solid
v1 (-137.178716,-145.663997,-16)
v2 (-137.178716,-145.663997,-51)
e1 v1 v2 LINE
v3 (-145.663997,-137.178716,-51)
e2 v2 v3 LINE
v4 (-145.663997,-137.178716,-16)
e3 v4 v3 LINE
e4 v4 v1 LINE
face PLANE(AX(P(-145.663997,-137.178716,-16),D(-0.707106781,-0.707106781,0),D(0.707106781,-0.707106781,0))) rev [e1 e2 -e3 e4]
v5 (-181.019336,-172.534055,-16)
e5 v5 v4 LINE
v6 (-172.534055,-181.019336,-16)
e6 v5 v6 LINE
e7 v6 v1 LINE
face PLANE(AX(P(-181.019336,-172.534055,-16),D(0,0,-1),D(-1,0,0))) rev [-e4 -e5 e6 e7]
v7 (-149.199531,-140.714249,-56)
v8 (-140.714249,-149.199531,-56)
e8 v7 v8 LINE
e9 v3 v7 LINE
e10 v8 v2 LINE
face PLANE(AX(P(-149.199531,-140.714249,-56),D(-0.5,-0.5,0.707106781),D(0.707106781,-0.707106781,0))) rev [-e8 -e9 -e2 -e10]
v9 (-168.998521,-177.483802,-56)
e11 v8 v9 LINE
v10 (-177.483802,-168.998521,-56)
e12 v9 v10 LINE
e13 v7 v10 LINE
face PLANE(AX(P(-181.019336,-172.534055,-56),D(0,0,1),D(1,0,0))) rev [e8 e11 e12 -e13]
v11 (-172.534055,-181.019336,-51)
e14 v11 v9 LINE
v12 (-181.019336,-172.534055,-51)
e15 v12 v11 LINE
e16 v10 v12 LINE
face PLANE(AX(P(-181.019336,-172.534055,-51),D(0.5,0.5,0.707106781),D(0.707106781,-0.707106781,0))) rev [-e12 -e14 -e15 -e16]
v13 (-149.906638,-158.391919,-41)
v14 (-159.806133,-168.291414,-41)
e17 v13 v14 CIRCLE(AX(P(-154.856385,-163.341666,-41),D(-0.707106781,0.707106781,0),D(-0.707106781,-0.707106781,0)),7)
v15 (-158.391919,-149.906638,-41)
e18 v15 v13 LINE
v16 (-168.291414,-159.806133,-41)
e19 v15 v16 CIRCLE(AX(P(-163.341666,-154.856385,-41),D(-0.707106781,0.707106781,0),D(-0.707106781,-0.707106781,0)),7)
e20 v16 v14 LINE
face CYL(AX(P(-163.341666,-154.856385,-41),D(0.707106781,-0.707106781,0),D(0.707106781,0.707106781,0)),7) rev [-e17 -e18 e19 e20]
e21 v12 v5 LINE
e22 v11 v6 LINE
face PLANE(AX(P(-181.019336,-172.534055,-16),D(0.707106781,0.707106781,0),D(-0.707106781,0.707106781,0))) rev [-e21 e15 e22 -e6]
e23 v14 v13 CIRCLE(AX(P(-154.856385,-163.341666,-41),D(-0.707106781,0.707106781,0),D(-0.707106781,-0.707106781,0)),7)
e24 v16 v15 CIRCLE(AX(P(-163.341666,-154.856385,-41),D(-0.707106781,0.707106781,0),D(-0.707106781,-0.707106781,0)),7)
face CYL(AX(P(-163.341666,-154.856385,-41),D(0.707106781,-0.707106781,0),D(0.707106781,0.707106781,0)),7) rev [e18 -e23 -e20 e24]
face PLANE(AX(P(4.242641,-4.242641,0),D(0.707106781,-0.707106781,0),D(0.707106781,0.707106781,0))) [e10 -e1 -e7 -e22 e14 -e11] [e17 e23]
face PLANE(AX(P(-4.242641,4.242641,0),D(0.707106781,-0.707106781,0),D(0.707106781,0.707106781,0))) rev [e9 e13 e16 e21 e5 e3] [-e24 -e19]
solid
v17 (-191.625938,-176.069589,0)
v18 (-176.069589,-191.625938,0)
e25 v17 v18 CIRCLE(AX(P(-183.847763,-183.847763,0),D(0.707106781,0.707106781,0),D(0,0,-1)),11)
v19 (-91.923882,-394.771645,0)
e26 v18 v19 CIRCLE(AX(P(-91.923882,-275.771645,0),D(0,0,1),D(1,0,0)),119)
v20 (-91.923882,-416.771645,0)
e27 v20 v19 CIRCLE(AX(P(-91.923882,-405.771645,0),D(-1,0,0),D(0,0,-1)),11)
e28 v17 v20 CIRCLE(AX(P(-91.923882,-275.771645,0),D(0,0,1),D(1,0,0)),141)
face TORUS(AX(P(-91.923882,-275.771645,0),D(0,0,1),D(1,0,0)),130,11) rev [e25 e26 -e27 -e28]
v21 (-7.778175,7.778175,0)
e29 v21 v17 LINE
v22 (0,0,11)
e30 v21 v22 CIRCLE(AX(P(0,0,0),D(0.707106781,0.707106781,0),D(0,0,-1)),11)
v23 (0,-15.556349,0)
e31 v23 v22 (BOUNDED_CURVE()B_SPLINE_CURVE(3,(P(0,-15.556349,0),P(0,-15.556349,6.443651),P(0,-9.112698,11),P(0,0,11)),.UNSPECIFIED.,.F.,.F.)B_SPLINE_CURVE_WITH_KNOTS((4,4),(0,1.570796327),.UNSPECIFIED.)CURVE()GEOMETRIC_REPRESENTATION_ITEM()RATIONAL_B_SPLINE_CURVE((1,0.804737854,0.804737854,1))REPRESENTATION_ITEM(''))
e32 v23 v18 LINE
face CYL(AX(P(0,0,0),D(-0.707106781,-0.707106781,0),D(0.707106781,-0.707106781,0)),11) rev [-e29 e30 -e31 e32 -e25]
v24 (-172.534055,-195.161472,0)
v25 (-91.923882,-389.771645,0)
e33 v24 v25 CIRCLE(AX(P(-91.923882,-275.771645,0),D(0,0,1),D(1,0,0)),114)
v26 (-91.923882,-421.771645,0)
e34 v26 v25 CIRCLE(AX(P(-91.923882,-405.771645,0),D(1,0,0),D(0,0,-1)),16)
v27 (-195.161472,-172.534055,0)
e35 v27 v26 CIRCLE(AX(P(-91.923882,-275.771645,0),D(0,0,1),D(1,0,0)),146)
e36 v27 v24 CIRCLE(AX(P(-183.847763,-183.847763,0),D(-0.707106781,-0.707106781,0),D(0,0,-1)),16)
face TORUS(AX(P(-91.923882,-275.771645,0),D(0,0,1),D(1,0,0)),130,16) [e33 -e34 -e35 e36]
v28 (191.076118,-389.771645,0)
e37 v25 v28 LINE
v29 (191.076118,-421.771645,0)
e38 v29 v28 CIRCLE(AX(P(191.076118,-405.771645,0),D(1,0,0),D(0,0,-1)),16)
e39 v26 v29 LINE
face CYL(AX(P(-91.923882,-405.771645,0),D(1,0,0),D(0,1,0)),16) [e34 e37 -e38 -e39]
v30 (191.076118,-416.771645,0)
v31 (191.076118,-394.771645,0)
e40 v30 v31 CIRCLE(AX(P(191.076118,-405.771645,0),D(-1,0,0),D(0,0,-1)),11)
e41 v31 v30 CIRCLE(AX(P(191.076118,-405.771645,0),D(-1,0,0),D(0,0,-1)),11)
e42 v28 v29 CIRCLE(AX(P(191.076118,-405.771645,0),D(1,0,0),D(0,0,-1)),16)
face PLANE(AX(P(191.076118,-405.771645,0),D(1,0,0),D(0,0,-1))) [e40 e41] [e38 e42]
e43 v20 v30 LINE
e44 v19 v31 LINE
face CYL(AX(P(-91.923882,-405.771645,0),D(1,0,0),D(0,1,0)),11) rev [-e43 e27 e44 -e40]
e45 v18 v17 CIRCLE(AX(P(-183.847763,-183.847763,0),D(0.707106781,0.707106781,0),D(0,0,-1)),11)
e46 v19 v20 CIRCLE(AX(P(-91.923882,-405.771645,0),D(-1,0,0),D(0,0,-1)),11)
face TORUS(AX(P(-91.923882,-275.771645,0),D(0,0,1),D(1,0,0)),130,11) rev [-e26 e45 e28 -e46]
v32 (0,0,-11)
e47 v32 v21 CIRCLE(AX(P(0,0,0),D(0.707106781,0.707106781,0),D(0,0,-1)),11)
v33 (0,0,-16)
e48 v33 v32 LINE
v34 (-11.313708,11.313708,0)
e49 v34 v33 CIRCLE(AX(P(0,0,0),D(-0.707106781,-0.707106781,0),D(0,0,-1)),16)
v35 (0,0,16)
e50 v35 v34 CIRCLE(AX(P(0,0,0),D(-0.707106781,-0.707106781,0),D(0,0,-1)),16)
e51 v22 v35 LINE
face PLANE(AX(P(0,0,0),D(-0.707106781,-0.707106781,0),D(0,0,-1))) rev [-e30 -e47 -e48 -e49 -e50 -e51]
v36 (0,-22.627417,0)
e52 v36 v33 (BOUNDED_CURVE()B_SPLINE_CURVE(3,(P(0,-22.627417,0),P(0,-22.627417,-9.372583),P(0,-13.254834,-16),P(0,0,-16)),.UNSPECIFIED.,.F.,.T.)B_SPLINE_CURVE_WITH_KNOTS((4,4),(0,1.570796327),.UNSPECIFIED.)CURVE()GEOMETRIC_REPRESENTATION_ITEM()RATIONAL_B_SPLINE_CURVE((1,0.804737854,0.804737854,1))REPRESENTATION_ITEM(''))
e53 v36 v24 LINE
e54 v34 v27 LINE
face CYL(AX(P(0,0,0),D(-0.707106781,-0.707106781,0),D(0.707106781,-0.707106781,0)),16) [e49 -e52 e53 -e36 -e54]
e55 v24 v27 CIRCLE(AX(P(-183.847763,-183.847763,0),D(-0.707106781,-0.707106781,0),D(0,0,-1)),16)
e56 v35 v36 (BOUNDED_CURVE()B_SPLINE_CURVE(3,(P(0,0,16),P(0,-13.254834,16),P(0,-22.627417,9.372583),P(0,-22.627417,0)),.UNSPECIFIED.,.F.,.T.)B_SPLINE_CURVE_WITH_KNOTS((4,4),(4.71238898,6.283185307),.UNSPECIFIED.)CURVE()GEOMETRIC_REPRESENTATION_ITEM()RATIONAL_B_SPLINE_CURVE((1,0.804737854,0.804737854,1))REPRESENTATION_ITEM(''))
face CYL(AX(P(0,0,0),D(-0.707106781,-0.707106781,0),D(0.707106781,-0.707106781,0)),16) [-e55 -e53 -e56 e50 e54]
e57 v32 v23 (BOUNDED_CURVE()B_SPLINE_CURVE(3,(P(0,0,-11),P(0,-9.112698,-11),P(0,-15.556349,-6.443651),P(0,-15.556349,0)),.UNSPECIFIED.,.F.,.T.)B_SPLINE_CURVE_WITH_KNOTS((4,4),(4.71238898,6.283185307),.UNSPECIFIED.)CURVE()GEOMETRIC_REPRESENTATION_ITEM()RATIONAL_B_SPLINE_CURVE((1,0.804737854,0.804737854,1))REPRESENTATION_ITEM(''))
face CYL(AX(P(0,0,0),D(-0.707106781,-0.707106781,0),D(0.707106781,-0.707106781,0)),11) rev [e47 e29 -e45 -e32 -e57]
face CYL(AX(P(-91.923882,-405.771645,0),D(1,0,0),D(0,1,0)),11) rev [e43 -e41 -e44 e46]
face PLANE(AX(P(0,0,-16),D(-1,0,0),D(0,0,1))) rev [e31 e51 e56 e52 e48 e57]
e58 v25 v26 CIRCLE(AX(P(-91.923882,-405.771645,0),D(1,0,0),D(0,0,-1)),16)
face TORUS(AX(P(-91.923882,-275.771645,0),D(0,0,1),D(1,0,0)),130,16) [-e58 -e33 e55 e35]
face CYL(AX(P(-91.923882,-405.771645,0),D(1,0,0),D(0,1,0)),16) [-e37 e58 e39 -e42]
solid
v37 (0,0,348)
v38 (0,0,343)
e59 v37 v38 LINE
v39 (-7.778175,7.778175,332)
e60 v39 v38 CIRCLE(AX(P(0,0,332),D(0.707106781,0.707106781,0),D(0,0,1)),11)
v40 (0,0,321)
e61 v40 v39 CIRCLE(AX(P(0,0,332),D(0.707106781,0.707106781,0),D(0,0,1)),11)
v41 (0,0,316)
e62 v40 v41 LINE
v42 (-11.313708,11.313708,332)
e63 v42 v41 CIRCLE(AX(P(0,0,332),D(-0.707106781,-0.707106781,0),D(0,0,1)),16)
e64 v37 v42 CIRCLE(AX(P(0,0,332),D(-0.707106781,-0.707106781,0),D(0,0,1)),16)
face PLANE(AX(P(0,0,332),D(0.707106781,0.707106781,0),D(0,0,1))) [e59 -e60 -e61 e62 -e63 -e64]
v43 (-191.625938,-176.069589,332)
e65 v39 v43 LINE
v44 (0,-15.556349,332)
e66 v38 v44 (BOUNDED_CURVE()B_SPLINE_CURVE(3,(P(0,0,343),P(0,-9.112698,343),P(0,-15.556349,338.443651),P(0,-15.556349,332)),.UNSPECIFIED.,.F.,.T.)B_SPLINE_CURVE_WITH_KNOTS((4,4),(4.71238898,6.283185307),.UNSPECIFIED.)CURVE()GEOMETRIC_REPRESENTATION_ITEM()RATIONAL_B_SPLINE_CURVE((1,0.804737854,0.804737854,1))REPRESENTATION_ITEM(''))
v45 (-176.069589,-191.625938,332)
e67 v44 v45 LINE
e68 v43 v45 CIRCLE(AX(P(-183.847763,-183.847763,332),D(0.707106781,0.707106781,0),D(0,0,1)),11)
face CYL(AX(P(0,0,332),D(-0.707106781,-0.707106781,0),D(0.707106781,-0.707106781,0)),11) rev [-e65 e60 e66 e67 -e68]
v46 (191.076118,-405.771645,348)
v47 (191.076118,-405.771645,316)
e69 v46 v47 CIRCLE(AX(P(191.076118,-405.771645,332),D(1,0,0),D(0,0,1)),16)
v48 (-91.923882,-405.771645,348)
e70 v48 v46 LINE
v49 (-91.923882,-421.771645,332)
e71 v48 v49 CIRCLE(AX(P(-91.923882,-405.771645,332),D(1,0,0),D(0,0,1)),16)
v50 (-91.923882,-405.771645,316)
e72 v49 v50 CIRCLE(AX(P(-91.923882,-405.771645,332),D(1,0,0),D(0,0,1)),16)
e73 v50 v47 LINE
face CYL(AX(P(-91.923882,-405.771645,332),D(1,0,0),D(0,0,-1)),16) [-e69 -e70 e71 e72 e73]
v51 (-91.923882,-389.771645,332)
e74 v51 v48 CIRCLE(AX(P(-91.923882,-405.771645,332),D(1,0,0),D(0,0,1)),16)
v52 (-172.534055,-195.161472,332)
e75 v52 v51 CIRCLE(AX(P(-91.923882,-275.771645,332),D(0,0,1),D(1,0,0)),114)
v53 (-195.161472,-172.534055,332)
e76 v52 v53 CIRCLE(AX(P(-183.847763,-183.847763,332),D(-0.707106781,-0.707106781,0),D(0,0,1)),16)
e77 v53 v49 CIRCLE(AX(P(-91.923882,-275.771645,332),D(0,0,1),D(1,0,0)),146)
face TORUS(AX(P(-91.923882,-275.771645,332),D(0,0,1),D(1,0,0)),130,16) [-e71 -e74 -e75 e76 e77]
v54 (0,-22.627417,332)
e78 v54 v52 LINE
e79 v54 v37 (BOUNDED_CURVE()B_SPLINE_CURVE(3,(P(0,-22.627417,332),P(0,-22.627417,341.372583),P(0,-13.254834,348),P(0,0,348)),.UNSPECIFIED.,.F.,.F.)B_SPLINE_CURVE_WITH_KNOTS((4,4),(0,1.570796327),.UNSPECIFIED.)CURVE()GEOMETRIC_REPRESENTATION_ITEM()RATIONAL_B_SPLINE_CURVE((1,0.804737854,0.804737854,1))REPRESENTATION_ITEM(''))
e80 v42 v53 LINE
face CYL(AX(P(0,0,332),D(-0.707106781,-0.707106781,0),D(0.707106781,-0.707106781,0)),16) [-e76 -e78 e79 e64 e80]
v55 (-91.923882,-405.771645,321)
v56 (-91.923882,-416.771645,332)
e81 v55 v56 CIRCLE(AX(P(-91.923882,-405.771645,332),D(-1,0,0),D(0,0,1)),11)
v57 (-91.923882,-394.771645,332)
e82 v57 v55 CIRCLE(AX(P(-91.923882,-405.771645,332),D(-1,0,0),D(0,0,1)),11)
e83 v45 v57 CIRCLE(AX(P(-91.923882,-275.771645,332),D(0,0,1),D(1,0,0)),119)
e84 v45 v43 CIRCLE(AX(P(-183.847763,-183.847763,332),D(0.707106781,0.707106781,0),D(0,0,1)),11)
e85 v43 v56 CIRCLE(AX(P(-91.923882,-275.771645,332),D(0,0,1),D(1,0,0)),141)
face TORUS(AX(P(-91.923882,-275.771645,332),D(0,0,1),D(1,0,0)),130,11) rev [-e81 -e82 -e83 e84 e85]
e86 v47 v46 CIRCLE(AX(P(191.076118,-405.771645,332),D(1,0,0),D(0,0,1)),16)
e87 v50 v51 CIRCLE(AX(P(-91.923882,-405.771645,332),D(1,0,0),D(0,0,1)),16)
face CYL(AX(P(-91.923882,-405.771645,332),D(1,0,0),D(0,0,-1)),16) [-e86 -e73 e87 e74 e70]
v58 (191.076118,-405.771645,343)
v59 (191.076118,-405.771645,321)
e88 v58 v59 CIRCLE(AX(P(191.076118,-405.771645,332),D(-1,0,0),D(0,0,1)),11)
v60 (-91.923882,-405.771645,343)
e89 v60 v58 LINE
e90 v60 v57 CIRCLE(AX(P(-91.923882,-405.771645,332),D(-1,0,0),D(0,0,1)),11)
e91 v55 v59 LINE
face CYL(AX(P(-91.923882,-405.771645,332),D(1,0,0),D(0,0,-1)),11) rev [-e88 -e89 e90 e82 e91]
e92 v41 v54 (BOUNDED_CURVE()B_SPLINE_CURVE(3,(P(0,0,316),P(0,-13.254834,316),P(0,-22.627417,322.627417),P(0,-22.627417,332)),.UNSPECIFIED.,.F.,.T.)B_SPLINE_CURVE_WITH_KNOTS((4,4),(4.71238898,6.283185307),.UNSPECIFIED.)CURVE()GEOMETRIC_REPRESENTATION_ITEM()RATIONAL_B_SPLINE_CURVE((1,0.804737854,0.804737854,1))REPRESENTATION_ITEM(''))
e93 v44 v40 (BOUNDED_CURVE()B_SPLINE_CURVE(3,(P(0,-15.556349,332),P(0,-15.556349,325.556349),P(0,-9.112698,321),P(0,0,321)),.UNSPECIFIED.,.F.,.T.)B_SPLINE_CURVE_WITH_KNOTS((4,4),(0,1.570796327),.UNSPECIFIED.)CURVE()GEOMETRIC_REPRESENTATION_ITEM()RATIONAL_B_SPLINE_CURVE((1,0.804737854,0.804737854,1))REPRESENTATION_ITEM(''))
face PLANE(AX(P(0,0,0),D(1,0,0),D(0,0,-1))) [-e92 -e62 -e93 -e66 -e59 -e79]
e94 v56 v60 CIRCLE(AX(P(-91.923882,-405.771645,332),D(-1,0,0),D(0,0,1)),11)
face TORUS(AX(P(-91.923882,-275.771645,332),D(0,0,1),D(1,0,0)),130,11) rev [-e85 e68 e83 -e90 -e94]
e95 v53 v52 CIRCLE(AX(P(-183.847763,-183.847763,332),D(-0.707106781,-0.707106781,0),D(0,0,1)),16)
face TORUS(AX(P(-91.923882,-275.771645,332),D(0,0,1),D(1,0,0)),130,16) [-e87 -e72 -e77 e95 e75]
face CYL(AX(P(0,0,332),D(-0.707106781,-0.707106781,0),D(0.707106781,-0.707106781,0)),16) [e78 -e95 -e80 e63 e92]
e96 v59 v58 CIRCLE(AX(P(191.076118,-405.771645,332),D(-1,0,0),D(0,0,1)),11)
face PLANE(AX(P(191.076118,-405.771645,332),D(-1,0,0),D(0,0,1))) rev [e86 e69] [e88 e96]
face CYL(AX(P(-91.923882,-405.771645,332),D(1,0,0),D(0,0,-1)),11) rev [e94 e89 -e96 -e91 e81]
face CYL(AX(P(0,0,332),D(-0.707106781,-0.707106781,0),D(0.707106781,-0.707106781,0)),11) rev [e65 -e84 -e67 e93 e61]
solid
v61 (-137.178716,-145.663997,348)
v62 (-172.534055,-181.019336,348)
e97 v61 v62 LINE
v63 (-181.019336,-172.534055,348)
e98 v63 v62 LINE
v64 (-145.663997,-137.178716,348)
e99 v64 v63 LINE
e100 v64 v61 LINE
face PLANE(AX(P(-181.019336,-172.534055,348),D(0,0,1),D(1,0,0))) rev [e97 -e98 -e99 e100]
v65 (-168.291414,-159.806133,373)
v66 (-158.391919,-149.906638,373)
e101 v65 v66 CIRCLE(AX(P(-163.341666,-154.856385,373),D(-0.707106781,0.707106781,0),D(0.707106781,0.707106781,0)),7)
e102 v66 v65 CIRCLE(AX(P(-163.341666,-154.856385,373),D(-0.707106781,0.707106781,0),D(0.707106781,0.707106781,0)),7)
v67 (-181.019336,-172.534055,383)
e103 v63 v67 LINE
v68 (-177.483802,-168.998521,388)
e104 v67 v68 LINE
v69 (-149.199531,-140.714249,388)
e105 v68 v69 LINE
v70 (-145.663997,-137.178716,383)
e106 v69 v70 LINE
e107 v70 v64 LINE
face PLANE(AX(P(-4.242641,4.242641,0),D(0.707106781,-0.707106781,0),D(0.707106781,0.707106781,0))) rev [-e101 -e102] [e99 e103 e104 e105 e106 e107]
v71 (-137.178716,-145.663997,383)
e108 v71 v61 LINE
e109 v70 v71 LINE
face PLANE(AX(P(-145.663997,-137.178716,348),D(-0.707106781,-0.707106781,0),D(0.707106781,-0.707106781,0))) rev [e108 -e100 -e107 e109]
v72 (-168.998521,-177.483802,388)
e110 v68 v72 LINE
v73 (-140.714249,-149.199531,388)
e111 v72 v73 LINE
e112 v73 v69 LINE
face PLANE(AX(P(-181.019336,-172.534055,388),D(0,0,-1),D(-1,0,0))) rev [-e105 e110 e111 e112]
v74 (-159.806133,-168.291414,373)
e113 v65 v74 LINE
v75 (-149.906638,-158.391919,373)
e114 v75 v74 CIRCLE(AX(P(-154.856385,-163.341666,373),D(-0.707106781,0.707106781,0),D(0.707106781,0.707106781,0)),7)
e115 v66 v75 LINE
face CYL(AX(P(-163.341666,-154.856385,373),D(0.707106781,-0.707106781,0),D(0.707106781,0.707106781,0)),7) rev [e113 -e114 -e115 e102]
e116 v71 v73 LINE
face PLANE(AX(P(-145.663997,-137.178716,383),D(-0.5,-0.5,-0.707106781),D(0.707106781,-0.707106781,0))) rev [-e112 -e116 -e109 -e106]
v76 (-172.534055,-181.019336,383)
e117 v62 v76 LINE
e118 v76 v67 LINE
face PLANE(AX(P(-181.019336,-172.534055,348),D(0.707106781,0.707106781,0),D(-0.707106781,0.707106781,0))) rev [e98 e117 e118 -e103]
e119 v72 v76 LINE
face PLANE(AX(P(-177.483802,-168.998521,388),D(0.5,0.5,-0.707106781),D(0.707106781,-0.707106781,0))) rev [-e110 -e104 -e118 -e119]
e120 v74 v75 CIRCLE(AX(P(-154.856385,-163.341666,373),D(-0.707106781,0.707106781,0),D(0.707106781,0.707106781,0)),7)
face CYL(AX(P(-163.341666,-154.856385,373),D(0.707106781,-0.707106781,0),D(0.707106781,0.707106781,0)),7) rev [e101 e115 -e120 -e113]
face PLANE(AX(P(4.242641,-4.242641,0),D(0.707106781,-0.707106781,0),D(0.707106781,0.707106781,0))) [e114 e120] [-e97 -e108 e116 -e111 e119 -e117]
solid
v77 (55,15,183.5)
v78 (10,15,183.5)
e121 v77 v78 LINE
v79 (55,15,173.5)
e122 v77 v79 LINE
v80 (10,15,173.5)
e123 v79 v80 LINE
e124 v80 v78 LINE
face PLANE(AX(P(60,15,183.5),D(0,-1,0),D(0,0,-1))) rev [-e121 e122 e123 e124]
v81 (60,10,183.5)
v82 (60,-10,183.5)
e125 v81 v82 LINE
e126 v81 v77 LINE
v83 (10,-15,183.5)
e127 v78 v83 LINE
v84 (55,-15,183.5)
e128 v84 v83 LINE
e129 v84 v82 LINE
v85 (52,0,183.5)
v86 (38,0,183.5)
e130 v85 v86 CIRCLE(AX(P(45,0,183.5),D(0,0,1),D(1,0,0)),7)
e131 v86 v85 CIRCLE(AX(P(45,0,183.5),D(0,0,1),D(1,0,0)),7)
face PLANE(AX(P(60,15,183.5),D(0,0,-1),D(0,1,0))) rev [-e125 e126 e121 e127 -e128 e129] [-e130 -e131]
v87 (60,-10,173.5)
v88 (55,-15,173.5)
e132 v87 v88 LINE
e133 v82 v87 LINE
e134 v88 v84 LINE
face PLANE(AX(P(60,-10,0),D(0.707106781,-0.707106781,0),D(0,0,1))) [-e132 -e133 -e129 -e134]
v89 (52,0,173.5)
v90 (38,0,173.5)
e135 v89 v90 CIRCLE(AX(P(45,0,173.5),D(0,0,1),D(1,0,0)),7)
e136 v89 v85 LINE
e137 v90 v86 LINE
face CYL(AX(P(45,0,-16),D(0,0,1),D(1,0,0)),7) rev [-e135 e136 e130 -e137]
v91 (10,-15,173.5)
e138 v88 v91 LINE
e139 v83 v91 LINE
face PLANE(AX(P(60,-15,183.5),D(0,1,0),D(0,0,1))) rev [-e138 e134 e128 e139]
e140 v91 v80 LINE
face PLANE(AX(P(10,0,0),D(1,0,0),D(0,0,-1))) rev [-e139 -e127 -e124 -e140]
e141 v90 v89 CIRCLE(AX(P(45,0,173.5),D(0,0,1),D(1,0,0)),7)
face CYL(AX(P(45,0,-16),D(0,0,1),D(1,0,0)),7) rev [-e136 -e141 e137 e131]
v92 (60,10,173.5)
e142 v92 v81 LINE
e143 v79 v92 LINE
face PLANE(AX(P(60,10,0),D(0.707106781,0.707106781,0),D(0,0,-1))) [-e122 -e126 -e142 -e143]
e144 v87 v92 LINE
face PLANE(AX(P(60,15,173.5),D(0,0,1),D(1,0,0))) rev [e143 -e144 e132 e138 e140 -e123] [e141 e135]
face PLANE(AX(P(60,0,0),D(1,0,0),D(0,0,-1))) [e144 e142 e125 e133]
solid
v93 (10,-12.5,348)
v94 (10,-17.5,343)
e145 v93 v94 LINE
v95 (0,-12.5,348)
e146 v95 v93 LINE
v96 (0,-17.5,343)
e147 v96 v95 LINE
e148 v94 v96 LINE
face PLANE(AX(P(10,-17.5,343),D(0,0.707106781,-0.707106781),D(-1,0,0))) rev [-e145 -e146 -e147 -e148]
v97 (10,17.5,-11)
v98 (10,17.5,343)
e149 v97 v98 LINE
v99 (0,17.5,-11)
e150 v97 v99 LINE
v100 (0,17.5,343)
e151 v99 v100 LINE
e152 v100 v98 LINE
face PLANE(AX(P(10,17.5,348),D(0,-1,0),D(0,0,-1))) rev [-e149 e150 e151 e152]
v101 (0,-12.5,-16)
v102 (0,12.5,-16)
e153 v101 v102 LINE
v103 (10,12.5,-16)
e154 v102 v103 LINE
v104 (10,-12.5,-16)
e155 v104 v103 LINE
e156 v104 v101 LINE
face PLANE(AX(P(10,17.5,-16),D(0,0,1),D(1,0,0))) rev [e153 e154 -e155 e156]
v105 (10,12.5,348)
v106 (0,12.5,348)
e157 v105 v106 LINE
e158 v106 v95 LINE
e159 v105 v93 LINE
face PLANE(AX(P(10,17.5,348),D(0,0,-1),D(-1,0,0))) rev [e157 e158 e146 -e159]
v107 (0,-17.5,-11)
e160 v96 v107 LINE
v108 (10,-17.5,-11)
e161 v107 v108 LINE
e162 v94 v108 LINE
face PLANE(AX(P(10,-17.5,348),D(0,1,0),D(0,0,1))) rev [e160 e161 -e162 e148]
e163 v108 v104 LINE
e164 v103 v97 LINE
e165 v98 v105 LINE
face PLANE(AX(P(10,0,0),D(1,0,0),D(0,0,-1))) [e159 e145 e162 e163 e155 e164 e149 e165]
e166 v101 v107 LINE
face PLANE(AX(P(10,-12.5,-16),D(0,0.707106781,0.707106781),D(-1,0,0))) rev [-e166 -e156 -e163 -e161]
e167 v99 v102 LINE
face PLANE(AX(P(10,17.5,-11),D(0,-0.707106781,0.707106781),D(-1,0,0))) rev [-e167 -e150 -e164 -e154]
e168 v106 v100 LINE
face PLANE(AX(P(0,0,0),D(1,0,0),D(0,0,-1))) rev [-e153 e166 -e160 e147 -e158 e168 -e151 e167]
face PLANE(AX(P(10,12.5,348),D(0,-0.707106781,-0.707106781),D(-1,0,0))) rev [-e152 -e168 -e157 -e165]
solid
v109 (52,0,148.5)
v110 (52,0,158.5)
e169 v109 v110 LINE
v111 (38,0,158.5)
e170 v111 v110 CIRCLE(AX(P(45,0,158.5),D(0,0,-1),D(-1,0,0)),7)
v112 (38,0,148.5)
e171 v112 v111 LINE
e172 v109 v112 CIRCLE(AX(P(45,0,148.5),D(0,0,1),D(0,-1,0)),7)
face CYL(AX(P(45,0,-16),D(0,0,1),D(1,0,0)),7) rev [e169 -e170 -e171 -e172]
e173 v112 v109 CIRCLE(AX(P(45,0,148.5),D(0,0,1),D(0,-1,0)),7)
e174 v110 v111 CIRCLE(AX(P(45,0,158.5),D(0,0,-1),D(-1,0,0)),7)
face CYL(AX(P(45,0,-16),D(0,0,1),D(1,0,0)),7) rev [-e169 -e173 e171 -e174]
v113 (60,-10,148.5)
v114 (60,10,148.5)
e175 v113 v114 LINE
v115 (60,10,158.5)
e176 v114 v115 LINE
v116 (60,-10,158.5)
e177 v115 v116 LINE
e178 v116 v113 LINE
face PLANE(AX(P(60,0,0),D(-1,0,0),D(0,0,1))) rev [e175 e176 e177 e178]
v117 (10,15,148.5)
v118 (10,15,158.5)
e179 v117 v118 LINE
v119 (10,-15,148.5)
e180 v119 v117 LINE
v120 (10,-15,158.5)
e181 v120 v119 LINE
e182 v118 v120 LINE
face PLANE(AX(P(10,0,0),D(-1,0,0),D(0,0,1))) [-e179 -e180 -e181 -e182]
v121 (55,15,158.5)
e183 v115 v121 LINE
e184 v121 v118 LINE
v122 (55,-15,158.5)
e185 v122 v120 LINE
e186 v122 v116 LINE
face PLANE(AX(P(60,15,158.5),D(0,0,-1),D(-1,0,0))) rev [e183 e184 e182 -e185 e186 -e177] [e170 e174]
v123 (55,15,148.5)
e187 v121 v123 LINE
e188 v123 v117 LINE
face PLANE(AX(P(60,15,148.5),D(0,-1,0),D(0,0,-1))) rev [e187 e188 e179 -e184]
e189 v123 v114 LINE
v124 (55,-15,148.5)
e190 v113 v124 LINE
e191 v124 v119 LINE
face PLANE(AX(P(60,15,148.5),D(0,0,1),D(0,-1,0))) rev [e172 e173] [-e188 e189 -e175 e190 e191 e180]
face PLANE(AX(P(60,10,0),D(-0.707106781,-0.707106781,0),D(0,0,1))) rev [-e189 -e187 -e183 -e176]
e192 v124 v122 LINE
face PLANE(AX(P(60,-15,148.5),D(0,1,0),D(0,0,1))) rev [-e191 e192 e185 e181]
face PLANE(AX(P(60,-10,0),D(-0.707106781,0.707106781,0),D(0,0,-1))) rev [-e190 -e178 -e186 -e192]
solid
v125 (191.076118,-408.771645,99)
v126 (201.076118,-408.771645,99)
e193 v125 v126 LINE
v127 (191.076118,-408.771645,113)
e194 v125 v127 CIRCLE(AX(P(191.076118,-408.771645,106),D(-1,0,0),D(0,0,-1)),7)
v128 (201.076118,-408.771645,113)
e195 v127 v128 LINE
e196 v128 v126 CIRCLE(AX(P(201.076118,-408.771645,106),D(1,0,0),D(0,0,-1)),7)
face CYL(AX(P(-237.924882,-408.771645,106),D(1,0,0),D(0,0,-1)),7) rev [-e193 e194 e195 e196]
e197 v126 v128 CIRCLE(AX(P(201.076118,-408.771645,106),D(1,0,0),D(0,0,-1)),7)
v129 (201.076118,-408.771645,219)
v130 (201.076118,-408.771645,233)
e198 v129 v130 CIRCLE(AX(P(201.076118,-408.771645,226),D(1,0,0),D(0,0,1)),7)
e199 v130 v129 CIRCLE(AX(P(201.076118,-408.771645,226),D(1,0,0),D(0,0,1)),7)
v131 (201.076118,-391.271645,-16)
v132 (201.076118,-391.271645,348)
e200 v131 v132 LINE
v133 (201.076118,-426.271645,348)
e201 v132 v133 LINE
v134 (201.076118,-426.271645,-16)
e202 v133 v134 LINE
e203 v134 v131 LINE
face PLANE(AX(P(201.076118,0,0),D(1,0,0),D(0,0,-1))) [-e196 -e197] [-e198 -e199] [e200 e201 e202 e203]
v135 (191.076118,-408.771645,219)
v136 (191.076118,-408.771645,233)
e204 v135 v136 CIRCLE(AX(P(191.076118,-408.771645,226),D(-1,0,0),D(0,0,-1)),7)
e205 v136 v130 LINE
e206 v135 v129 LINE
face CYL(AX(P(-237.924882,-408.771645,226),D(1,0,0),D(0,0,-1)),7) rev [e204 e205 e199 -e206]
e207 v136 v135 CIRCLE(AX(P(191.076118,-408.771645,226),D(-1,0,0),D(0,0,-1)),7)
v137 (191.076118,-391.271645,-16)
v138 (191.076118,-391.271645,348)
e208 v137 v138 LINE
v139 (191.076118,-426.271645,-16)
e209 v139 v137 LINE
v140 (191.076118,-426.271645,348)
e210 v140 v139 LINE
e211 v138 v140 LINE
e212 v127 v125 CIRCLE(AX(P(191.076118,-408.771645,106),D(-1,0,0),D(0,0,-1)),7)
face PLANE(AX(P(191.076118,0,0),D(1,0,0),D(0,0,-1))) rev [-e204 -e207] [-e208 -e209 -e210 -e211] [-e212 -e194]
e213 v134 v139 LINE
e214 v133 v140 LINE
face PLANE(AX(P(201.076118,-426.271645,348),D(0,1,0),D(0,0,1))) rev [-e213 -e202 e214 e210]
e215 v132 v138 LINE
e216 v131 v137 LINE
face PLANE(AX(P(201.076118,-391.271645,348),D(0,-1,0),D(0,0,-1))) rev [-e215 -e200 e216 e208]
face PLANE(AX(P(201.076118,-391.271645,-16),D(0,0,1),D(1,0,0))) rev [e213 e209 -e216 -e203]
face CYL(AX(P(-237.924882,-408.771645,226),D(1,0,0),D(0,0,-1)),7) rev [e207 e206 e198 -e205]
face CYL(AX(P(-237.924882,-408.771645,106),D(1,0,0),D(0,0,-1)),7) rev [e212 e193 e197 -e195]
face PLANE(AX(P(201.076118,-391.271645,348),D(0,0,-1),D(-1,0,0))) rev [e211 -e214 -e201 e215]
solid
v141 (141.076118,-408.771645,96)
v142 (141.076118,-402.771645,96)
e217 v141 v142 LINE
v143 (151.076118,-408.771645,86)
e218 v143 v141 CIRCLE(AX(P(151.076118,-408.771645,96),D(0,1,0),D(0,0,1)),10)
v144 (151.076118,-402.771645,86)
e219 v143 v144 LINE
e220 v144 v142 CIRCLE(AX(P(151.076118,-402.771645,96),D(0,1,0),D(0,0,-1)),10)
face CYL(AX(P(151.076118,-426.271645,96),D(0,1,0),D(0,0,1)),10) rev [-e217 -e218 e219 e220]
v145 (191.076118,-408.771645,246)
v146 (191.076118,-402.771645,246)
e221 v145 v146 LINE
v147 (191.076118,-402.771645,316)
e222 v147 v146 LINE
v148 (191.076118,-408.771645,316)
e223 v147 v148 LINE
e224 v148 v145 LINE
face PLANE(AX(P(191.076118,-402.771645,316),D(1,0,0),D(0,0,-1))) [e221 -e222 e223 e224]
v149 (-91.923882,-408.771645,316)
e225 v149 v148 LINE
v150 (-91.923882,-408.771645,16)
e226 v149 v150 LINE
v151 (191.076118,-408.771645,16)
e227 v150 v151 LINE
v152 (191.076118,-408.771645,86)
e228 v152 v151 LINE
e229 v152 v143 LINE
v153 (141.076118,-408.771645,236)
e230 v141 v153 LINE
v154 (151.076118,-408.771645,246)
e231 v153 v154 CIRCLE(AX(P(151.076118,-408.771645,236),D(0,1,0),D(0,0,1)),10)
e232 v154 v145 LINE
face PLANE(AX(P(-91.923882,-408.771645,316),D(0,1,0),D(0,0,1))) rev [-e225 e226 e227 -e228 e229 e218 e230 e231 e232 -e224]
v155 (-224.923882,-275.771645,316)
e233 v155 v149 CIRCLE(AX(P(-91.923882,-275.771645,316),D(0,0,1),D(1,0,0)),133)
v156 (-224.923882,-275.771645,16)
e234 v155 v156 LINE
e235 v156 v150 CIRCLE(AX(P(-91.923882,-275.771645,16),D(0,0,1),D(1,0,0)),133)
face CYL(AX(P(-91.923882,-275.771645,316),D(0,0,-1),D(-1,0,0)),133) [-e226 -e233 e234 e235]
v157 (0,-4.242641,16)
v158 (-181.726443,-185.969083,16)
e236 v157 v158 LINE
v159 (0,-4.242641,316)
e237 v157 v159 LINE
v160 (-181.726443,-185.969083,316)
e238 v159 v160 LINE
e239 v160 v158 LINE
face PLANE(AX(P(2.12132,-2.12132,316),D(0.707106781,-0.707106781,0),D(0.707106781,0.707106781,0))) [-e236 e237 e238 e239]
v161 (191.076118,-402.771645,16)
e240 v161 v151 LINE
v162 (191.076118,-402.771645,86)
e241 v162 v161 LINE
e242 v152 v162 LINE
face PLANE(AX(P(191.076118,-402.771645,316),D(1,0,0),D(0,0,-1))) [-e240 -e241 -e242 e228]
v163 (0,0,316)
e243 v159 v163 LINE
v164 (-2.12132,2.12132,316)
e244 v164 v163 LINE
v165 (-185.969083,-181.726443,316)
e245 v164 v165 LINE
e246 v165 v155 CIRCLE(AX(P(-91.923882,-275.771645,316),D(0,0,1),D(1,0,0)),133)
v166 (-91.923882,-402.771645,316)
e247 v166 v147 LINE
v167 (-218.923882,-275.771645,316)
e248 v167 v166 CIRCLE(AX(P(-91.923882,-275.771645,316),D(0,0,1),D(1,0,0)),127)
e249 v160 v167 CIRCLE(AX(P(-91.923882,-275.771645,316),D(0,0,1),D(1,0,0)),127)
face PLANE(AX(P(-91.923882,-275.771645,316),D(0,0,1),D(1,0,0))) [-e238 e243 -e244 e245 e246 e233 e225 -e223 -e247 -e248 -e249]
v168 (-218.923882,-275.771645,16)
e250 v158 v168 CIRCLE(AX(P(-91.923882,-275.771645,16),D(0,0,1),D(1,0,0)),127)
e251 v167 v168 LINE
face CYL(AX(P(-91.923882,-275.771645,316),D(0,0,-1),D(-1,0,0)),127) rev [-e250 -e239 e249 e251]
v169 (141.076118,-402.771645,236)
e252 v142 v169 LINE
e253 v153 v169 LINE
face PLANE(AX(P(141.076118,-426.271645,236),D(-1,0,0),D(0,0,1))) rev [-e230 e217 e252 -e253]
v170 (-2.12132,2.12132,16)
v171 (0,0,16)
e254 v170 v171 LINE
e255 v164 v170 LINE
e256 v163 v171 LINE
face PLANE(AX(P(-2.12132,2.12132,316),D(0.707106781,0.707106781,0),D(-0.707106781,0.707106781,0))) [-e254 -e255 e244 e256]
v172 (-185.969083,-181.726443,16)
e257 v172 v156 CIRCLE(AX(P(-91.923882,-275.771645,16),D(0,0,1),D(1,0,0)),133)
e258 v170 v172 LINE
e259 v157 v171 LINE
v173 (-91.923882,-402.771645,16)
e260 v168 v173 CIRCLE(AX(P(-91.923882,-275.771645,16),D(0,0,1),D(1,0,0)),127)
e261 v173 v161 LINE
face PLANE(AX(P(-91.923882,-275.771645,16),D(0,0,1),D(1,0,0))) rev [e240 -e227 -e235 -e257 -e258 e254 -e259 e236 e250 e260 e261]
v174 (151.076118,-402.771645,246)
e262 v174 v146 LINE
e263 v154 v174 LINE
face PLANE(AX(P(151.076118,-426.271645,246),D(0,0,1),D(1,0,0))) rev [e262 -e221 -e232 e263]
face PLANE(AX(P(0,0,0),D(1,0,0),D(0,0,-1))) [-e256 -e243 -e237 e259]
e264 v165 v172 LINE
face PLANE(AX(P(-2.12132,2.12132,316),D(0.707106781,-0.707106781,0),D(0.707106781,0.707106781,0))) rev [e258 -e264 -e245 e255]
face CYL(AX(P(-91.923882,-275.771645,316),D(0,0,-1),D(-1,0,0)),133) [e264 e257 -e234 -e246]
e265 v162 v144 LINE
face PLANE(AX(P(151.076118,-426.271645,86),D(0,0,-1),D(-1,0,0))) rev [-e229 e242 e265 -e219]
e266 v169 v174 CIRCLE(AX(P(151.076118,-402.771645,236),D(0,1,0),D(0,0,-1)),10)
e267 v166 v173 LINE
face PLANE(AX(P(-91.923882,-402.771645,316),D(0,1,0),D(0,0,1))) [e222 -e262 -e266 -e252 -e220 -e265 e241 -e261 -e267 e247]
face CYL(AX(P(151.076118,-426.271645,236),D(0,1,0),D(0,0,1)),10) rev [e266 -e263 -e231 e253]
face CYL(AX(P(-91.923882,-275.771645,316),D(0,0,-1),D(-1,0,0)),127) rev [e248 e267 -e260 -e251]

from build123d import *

# Parameters (mm, degrees)
SKETCH_2_R               = 16
SKETCH_2_R_2             = 11
CUT_EXTRUDE_1_DEPTH      = 485.515318427
CUT_EXTRUDE_1_DEPTH_BACK = 485.515318427
SKETCH_4_W               = 55.642342567
SKETCH_4_H               = 67.933254927
EXTRUDE_START            = 16
EXTRUDE_2_DEPTH          = 300
SKETCH_7_R               = 16
SKETCH_7_R_2             = 11
SKETCH_9_W               = 513.497861872
SKETCH_9_H               = 78.296499381
CUT_EXTRUDE_2_DEPTH      = 597.324654745
SKETCH_10_W              = 364
SKETCH_10_H              = 35
EXTRUDE_2_2_DEPTH        = 10
SKETCH_11_W              = 364
SKETCH_11_H              = 35
EXTRUDE_4_DEPTH          = 10
CHAMFER_1_SIZE           = 5
CUT_EXTRUDE_4_DEPTH      = 596.26467125
SKETCH_14_R              = 7
CUT_EXTRUDE_5_DEPTH      = 10
SKETCH_15_W              = 10
SKETCH_15_H              = 30
EXTRUDE_5_DEPTH          = 50
EXTRUDE_5_2_DEPTH        = 50
CHAMFER_2_SIZE           = 5
CHAMFER_3_SIZE           = 5
SKETCH_16_R              = 7
CUT_EXTRUDE_6_DEPTH      = 528.366607347
SKETCH_18_W              = 50
SKETCH_18_H              = 40
SKETCH_18_R              = 7
EXTRUDE_6_DEPTH          = 6
EXTRUDE_6_2_DEPTH        = 6
CHAMFER_4_SIZE           = 5
CHAMFER_5_SIZE           = 5


with BuildPart() as part:
    # 扫描1: sweep along a path in 草图1
    with BuildLine(Plane.XY) as sweep_1_path:
        Line((0, 0), (-183.847763109, -183.847763109))
        ThreePointArc((-183.847763109, -183.847763109), (-212.028220781, -325.52049087), (-91.923881554, -405.771644663))
        Line((-91.923881554, -405.771644663), (191.076118446, -405.771644663))
    # 草图2 → 扫描1 (sweep)
    with BuildSketch(Plane(origin=(191.076118446, 0, 0), x_dir=(0, 0, -1), z_dir=(1, 0, 0))):
        with Locations((0, -405.771644663)):
            Circle(SKETCH_2_R)
        with Locations((0, -405.771644663)):
            Circle(SKETCH_2_R_2, mode=Mode.SUBTRACT)
    sweep(path=sweep_1_path.line)

    # 草图4 → 切除-拉伸1 (cut, two sides: drawn at the far end of the back side and taken through both)
    with BuildSketch(Plane.XY.offset(-CUT_EXTRUDE_1_DEPTH_BACK)):
        with Locations((27.821171284, -33.966627464)):
            Rectangle(SKETCH_4_W, SKETCH_4_H)
    extrude(amount=CUT_EXTRUDE_1_DEPTH + CUT_EXTRUDE_1_DEPTH_BACK, mode=Mode.SUBTRACT)


with BuildPart() as body_2:
    # 草图6 → Extrude 2 (new body)
    with BuildSketch(Plane.XY.offset(EXTRUDE_START)):
        with BuildLine():
            Line((-2.121320344, 2.121320344), (-185.969083452, -181.726442765))
            ThreePointArc((-185.969083452, -181.726442765), (-214.799859378, -326.668541167), (-91.923881554, -408.771644663))
            Line((-91.923881554, -408.771644663), (191.076118446, -408.771644663))
            Line((191.076118446, -408.771644663), (191.076118446, -402.771644663))
            Line((191.076118446, -402.771644663), (-91.923881554, -402.771644663))
            ThreePointArc((-91.923881554, -402.771644663), (-209.256582183, -324.372440573), (-181.726442765, -185.969083452))
            Line((-181.726442765, -185.969083452), (2.121320344, -2.121320344))
            Line((2.121320344, -2.121320344), (-2.121320344, 2.121320344))
        make_face()
    extrude(amount=EXTRUDE_2_DEPTH)


with BuildPart() as body_3:
    # 扫描2: sweep along a path in 草图8
    with BuildLine(Plane.XY.offset(332)) as sweep_2_path:
        Line((0, 0), (-183.847763109, -183.847763109))
        ThreePointArc((-183.847763109, -183.847763109), (-212.028220781, -325.52049087), (-91.923881554, -405.771644663))
        Line((-91.923881554, -405.771644663), (191.076118446, -405.771644663))
    # 草图7 → 扫描2 (sweep)
    with BuildSketch(Plane(origin=(191.076118446, 0, 0), x_dir=(0, 0, -1), z_dir=(1, 0, 0))):
        with Locations((-332, -405.771644663)):
            Circle(SKETCH_7_R)
        with Locations((-332, -405.771644663)):
            Circle(SKETCH_7_R_2, mode=Mode.SUBTRACT)
    sweep(path=sweep_2_path.line)


with BuildPart() as cut_extrude_2_tool:
    # 草图9 → 切除-拉伸2 (new, through all)
    with BuildSketch(Plane(origin=(0, 0, 0), x_dir=(0, 0, -1), z_dir=(1, 0, 0))):
        with Locations((-166, -2.121320344)):
            Rectangle(SKETCH_9_W, SKETCH_9_H)
    extrude(amount=CUT_EXTRUDE_2_DEPTH)


with BuildPart() as body_2_1:
    add(body_2.part)

    # 切除-拉伸2: cut by cut_extrude_2_tool
    add(cut_extrude_2_tool.part, mode=Mode.SUBTRACT)

    # 草图13 → 切除-拉伸4 (cut, through all)
    with BuildSketch(Plane(origin=(0, -402.771644663, 0), x_dir=(1, 0, 0), z_dir=(0, 1, 0))):
        with BuildLine():
            Line((151.076118446, -246), (191.076118446, -246))
            Line((191.076118446, -246), (191.076118446, -86))
            Line((191.076118446, -86), (151.076118446, -86))
            ThreePointArc((151.076118446, -86), (144.005050634, -88.928932188), (141.076118446, -96))
            Line((141.076118446, -96), (141.076118446, -236))
            ThreePointArc((141.076118446, -236), (144.005050634, -243.071067812), (151.076118446, -246))
        make_face()
    extrude(amount=-CUT_EXTRUDE_4_DEPTH, mode=Mode.SUBTRACT)


with BuildPart() as body_3_1:
    add(body_3.part)

    # 切除-拉伸2: cut by cut_extrude_2_tool
    add(cut_extrude_2_tool.part, mode=Mode.SUBTRACT)


with BuildPart() as body_4:
    # 草图10 → Extrude 2 2 (new body)
    with BuildSketch(Plane(origin=(0, 0, 0), x_dir=(0, 0, -1), z_dir=(1, 0, 0))):
        with Locations((-166, 0)):
            Rectangle(SKETCH_10_W, SKETCH_10_H)
    extrude(amount=EXTRUDE_2_2_DEPTH)

    # 倒角1
    chamfer_1_edges = [body_4.edges().sort_by_distance(p)[0] for p in [
        (5, -17.5, -16),
        (5, -17.5, 348),
        (5, 17.5, 348),
        (5, 17.5, -16),
    ]]
    chamfer(chamfer_1_edges, length=CHAMFER_1_SIZE)


with BuildPart() as body_5:
    # 草图11 → 凸台-拉伸4 (new body)
    with BuildSketch(Plane(origin=(191.076118446, 0, 0), x_dir=(0, 0, -1), z_dir=(1, 0, 0))):
        with Locations((-166, -408.771644663)):
            Rectangle(SKETCH_11_W, SKETCH_11_H)
    extrude(amount=EXTRUDE_4_DEPTH)

    # 草图14 → 切除-拉伸5 (cut)
    with BuildSketch(Plane(origin=(201.076118446, 0, 0), x_dir=(0, 0, -1), z_dir=(1, 0, 0))):
        with Locations((-106, -408.771644663)):
            Circle(SKETCH_14_R)
        with Locations((-226, -408.771644663)):
            Circle(SKETCH_14_R)
    extrude(amount=-CUT_EXTRUDE_5_DEPTH, mode=Mode.SUBTRACT)


with BuildPart() as body_6:
    # 草图15 → 凸台-拉伸5 (new body)
    with BuildSketch(Plane(origin=(10, 0, 0), x_dir=(0, 0, -1), z_dir=(1, 0, 0))):
        with Locations((-178.5, 0)):
            Rectangle(SKETCH_15_W, SKETCH_15_H)
    extrude(amount=EXTRUDE_5_DEPTH)

    # 倒角2
    chamfer_2_edges = [body_6.edges().sort_by_distance(p)[0] for p in [
        (60, -15, 178.5),
        (60, 15, 178.5),
    ]]
    chamfer(chamfer_2_edges, length=CHAMFER_2_SIZE)


with BuildPart() as body_7:
    # 草图15 → Extrude 5 2 (new body)
    with BuildSketch(Plane(origin=(10, 0, 0), x_dir=(0, 0, -1), z_dir=(1, 0, 0))):
        with Locations((-153.5, 0)):
            Rectangle(SKETCH_15_W, SKETCH_15_H)
    extrude(amount=EXTRUDE_5_2_DEPTH)

    # 倒角3
    chamfer_3_edges = [body_7.edges().sort_by_distance(p)[0] for p in [
        (60, -15, 153.5),
        (60, 15, 153.5),
    ]]
    chamfer(chamfer_3_edges, length=CHAMFER_3_SIZE)


with BuildPart() as cut_extrude_6_tool:
    # 草图16 → 切除-拉伸6 (new, through all)
    with BuildSketch(Plane.XY.offset(183.5)):
        with Locations((45, 0)):
            Circle(SKETCH_16_R)
    extrude(amount=-CUT_EXTRUDE_6_DEPTH)


with BuildPart() as body_6_1:
    add(body_6.part)

    # 切除-拉伸6: cut by cut_extrude_6_tool
    add(cut_extrude_6_tool.part, mode=Mode.SUBTRACT)


with BuildPart() as body_7_1:
    add(body_7.part)

    # 切除-拉伸6: cut by cut_extrude_6_tool
    add(cut_extrude_6_tool.part, mode=Mode.SUBTRACT)


with BuildPart() as body_8:
    # 草图18 → 凸台-拉伸6 (new, symmetric)
    with BuildSketch(Plane(origin=(0, 0, 0), x_dir=(0.7071067811865511, 0.7071067811865439, 0), z_dir=(-0.7071067811865439, 0.7071067811865511, 0))):
        with Locations((-225, 36)):
            Rectangle(SKETCH_18_W, SKETCH_18_H)
        with Locations(Location((-225, 41, 0), (0, 0, 180))):
            Circle(SKETCH_18_R, mode=Mode.SUBTRACT)
    extrude(amount=EXTRUDE_6_DEPTH, both=True)

    # 倒角4
    chamfer_4_edges = [body_8.edges().sort_by_distance(p)[0] for p in [
        (-176.776695297, -176.776695297, -56),
        (-141.421356237, -141.421356237, -56),
    ]]
    chamfer(chamfer_4_edges, length=CHAMFER_4_SIZE)


with BuildPart() as body_9:
    # 草图18 → Extrude 6 2 (new, symmetric)
    with BuildSketch(Plane(origin=(0, 0, 0), x_dir=(0.7071067811865511, 0.7071067811865439, 0), z_dir=(-0.7071067811865439, 0.7071067811865511, 0))):
        with Locations((-225, -368)):
            Rectangle(SKETCH_18_W, SKETCH_18_H)
        with Locations((-225, -373)):
            Circle(SKETCH_18_R, mode=Mode.SUBTRACT)
    extrude(amount=EXTRUDE_6_2_DEPTH, both=True)

    # 倒角5
    chamfer_5_edges = [body_9.edges().sort_by_distance(p)[0] for p in [
        (-141.421356237, -141.421356237, 388),
        (-176.776695297, -176.776695297, 388),
    ]]
    chamfer(chamfer_5_edges, length=CHAMFER_5_SIZE)


solid = Compound([part.part, body_2_1.part, body_3_1.part, body_4.part, body_5.part, body_6_1.part, body_7_1.part, body_8.part, body_9.part])
